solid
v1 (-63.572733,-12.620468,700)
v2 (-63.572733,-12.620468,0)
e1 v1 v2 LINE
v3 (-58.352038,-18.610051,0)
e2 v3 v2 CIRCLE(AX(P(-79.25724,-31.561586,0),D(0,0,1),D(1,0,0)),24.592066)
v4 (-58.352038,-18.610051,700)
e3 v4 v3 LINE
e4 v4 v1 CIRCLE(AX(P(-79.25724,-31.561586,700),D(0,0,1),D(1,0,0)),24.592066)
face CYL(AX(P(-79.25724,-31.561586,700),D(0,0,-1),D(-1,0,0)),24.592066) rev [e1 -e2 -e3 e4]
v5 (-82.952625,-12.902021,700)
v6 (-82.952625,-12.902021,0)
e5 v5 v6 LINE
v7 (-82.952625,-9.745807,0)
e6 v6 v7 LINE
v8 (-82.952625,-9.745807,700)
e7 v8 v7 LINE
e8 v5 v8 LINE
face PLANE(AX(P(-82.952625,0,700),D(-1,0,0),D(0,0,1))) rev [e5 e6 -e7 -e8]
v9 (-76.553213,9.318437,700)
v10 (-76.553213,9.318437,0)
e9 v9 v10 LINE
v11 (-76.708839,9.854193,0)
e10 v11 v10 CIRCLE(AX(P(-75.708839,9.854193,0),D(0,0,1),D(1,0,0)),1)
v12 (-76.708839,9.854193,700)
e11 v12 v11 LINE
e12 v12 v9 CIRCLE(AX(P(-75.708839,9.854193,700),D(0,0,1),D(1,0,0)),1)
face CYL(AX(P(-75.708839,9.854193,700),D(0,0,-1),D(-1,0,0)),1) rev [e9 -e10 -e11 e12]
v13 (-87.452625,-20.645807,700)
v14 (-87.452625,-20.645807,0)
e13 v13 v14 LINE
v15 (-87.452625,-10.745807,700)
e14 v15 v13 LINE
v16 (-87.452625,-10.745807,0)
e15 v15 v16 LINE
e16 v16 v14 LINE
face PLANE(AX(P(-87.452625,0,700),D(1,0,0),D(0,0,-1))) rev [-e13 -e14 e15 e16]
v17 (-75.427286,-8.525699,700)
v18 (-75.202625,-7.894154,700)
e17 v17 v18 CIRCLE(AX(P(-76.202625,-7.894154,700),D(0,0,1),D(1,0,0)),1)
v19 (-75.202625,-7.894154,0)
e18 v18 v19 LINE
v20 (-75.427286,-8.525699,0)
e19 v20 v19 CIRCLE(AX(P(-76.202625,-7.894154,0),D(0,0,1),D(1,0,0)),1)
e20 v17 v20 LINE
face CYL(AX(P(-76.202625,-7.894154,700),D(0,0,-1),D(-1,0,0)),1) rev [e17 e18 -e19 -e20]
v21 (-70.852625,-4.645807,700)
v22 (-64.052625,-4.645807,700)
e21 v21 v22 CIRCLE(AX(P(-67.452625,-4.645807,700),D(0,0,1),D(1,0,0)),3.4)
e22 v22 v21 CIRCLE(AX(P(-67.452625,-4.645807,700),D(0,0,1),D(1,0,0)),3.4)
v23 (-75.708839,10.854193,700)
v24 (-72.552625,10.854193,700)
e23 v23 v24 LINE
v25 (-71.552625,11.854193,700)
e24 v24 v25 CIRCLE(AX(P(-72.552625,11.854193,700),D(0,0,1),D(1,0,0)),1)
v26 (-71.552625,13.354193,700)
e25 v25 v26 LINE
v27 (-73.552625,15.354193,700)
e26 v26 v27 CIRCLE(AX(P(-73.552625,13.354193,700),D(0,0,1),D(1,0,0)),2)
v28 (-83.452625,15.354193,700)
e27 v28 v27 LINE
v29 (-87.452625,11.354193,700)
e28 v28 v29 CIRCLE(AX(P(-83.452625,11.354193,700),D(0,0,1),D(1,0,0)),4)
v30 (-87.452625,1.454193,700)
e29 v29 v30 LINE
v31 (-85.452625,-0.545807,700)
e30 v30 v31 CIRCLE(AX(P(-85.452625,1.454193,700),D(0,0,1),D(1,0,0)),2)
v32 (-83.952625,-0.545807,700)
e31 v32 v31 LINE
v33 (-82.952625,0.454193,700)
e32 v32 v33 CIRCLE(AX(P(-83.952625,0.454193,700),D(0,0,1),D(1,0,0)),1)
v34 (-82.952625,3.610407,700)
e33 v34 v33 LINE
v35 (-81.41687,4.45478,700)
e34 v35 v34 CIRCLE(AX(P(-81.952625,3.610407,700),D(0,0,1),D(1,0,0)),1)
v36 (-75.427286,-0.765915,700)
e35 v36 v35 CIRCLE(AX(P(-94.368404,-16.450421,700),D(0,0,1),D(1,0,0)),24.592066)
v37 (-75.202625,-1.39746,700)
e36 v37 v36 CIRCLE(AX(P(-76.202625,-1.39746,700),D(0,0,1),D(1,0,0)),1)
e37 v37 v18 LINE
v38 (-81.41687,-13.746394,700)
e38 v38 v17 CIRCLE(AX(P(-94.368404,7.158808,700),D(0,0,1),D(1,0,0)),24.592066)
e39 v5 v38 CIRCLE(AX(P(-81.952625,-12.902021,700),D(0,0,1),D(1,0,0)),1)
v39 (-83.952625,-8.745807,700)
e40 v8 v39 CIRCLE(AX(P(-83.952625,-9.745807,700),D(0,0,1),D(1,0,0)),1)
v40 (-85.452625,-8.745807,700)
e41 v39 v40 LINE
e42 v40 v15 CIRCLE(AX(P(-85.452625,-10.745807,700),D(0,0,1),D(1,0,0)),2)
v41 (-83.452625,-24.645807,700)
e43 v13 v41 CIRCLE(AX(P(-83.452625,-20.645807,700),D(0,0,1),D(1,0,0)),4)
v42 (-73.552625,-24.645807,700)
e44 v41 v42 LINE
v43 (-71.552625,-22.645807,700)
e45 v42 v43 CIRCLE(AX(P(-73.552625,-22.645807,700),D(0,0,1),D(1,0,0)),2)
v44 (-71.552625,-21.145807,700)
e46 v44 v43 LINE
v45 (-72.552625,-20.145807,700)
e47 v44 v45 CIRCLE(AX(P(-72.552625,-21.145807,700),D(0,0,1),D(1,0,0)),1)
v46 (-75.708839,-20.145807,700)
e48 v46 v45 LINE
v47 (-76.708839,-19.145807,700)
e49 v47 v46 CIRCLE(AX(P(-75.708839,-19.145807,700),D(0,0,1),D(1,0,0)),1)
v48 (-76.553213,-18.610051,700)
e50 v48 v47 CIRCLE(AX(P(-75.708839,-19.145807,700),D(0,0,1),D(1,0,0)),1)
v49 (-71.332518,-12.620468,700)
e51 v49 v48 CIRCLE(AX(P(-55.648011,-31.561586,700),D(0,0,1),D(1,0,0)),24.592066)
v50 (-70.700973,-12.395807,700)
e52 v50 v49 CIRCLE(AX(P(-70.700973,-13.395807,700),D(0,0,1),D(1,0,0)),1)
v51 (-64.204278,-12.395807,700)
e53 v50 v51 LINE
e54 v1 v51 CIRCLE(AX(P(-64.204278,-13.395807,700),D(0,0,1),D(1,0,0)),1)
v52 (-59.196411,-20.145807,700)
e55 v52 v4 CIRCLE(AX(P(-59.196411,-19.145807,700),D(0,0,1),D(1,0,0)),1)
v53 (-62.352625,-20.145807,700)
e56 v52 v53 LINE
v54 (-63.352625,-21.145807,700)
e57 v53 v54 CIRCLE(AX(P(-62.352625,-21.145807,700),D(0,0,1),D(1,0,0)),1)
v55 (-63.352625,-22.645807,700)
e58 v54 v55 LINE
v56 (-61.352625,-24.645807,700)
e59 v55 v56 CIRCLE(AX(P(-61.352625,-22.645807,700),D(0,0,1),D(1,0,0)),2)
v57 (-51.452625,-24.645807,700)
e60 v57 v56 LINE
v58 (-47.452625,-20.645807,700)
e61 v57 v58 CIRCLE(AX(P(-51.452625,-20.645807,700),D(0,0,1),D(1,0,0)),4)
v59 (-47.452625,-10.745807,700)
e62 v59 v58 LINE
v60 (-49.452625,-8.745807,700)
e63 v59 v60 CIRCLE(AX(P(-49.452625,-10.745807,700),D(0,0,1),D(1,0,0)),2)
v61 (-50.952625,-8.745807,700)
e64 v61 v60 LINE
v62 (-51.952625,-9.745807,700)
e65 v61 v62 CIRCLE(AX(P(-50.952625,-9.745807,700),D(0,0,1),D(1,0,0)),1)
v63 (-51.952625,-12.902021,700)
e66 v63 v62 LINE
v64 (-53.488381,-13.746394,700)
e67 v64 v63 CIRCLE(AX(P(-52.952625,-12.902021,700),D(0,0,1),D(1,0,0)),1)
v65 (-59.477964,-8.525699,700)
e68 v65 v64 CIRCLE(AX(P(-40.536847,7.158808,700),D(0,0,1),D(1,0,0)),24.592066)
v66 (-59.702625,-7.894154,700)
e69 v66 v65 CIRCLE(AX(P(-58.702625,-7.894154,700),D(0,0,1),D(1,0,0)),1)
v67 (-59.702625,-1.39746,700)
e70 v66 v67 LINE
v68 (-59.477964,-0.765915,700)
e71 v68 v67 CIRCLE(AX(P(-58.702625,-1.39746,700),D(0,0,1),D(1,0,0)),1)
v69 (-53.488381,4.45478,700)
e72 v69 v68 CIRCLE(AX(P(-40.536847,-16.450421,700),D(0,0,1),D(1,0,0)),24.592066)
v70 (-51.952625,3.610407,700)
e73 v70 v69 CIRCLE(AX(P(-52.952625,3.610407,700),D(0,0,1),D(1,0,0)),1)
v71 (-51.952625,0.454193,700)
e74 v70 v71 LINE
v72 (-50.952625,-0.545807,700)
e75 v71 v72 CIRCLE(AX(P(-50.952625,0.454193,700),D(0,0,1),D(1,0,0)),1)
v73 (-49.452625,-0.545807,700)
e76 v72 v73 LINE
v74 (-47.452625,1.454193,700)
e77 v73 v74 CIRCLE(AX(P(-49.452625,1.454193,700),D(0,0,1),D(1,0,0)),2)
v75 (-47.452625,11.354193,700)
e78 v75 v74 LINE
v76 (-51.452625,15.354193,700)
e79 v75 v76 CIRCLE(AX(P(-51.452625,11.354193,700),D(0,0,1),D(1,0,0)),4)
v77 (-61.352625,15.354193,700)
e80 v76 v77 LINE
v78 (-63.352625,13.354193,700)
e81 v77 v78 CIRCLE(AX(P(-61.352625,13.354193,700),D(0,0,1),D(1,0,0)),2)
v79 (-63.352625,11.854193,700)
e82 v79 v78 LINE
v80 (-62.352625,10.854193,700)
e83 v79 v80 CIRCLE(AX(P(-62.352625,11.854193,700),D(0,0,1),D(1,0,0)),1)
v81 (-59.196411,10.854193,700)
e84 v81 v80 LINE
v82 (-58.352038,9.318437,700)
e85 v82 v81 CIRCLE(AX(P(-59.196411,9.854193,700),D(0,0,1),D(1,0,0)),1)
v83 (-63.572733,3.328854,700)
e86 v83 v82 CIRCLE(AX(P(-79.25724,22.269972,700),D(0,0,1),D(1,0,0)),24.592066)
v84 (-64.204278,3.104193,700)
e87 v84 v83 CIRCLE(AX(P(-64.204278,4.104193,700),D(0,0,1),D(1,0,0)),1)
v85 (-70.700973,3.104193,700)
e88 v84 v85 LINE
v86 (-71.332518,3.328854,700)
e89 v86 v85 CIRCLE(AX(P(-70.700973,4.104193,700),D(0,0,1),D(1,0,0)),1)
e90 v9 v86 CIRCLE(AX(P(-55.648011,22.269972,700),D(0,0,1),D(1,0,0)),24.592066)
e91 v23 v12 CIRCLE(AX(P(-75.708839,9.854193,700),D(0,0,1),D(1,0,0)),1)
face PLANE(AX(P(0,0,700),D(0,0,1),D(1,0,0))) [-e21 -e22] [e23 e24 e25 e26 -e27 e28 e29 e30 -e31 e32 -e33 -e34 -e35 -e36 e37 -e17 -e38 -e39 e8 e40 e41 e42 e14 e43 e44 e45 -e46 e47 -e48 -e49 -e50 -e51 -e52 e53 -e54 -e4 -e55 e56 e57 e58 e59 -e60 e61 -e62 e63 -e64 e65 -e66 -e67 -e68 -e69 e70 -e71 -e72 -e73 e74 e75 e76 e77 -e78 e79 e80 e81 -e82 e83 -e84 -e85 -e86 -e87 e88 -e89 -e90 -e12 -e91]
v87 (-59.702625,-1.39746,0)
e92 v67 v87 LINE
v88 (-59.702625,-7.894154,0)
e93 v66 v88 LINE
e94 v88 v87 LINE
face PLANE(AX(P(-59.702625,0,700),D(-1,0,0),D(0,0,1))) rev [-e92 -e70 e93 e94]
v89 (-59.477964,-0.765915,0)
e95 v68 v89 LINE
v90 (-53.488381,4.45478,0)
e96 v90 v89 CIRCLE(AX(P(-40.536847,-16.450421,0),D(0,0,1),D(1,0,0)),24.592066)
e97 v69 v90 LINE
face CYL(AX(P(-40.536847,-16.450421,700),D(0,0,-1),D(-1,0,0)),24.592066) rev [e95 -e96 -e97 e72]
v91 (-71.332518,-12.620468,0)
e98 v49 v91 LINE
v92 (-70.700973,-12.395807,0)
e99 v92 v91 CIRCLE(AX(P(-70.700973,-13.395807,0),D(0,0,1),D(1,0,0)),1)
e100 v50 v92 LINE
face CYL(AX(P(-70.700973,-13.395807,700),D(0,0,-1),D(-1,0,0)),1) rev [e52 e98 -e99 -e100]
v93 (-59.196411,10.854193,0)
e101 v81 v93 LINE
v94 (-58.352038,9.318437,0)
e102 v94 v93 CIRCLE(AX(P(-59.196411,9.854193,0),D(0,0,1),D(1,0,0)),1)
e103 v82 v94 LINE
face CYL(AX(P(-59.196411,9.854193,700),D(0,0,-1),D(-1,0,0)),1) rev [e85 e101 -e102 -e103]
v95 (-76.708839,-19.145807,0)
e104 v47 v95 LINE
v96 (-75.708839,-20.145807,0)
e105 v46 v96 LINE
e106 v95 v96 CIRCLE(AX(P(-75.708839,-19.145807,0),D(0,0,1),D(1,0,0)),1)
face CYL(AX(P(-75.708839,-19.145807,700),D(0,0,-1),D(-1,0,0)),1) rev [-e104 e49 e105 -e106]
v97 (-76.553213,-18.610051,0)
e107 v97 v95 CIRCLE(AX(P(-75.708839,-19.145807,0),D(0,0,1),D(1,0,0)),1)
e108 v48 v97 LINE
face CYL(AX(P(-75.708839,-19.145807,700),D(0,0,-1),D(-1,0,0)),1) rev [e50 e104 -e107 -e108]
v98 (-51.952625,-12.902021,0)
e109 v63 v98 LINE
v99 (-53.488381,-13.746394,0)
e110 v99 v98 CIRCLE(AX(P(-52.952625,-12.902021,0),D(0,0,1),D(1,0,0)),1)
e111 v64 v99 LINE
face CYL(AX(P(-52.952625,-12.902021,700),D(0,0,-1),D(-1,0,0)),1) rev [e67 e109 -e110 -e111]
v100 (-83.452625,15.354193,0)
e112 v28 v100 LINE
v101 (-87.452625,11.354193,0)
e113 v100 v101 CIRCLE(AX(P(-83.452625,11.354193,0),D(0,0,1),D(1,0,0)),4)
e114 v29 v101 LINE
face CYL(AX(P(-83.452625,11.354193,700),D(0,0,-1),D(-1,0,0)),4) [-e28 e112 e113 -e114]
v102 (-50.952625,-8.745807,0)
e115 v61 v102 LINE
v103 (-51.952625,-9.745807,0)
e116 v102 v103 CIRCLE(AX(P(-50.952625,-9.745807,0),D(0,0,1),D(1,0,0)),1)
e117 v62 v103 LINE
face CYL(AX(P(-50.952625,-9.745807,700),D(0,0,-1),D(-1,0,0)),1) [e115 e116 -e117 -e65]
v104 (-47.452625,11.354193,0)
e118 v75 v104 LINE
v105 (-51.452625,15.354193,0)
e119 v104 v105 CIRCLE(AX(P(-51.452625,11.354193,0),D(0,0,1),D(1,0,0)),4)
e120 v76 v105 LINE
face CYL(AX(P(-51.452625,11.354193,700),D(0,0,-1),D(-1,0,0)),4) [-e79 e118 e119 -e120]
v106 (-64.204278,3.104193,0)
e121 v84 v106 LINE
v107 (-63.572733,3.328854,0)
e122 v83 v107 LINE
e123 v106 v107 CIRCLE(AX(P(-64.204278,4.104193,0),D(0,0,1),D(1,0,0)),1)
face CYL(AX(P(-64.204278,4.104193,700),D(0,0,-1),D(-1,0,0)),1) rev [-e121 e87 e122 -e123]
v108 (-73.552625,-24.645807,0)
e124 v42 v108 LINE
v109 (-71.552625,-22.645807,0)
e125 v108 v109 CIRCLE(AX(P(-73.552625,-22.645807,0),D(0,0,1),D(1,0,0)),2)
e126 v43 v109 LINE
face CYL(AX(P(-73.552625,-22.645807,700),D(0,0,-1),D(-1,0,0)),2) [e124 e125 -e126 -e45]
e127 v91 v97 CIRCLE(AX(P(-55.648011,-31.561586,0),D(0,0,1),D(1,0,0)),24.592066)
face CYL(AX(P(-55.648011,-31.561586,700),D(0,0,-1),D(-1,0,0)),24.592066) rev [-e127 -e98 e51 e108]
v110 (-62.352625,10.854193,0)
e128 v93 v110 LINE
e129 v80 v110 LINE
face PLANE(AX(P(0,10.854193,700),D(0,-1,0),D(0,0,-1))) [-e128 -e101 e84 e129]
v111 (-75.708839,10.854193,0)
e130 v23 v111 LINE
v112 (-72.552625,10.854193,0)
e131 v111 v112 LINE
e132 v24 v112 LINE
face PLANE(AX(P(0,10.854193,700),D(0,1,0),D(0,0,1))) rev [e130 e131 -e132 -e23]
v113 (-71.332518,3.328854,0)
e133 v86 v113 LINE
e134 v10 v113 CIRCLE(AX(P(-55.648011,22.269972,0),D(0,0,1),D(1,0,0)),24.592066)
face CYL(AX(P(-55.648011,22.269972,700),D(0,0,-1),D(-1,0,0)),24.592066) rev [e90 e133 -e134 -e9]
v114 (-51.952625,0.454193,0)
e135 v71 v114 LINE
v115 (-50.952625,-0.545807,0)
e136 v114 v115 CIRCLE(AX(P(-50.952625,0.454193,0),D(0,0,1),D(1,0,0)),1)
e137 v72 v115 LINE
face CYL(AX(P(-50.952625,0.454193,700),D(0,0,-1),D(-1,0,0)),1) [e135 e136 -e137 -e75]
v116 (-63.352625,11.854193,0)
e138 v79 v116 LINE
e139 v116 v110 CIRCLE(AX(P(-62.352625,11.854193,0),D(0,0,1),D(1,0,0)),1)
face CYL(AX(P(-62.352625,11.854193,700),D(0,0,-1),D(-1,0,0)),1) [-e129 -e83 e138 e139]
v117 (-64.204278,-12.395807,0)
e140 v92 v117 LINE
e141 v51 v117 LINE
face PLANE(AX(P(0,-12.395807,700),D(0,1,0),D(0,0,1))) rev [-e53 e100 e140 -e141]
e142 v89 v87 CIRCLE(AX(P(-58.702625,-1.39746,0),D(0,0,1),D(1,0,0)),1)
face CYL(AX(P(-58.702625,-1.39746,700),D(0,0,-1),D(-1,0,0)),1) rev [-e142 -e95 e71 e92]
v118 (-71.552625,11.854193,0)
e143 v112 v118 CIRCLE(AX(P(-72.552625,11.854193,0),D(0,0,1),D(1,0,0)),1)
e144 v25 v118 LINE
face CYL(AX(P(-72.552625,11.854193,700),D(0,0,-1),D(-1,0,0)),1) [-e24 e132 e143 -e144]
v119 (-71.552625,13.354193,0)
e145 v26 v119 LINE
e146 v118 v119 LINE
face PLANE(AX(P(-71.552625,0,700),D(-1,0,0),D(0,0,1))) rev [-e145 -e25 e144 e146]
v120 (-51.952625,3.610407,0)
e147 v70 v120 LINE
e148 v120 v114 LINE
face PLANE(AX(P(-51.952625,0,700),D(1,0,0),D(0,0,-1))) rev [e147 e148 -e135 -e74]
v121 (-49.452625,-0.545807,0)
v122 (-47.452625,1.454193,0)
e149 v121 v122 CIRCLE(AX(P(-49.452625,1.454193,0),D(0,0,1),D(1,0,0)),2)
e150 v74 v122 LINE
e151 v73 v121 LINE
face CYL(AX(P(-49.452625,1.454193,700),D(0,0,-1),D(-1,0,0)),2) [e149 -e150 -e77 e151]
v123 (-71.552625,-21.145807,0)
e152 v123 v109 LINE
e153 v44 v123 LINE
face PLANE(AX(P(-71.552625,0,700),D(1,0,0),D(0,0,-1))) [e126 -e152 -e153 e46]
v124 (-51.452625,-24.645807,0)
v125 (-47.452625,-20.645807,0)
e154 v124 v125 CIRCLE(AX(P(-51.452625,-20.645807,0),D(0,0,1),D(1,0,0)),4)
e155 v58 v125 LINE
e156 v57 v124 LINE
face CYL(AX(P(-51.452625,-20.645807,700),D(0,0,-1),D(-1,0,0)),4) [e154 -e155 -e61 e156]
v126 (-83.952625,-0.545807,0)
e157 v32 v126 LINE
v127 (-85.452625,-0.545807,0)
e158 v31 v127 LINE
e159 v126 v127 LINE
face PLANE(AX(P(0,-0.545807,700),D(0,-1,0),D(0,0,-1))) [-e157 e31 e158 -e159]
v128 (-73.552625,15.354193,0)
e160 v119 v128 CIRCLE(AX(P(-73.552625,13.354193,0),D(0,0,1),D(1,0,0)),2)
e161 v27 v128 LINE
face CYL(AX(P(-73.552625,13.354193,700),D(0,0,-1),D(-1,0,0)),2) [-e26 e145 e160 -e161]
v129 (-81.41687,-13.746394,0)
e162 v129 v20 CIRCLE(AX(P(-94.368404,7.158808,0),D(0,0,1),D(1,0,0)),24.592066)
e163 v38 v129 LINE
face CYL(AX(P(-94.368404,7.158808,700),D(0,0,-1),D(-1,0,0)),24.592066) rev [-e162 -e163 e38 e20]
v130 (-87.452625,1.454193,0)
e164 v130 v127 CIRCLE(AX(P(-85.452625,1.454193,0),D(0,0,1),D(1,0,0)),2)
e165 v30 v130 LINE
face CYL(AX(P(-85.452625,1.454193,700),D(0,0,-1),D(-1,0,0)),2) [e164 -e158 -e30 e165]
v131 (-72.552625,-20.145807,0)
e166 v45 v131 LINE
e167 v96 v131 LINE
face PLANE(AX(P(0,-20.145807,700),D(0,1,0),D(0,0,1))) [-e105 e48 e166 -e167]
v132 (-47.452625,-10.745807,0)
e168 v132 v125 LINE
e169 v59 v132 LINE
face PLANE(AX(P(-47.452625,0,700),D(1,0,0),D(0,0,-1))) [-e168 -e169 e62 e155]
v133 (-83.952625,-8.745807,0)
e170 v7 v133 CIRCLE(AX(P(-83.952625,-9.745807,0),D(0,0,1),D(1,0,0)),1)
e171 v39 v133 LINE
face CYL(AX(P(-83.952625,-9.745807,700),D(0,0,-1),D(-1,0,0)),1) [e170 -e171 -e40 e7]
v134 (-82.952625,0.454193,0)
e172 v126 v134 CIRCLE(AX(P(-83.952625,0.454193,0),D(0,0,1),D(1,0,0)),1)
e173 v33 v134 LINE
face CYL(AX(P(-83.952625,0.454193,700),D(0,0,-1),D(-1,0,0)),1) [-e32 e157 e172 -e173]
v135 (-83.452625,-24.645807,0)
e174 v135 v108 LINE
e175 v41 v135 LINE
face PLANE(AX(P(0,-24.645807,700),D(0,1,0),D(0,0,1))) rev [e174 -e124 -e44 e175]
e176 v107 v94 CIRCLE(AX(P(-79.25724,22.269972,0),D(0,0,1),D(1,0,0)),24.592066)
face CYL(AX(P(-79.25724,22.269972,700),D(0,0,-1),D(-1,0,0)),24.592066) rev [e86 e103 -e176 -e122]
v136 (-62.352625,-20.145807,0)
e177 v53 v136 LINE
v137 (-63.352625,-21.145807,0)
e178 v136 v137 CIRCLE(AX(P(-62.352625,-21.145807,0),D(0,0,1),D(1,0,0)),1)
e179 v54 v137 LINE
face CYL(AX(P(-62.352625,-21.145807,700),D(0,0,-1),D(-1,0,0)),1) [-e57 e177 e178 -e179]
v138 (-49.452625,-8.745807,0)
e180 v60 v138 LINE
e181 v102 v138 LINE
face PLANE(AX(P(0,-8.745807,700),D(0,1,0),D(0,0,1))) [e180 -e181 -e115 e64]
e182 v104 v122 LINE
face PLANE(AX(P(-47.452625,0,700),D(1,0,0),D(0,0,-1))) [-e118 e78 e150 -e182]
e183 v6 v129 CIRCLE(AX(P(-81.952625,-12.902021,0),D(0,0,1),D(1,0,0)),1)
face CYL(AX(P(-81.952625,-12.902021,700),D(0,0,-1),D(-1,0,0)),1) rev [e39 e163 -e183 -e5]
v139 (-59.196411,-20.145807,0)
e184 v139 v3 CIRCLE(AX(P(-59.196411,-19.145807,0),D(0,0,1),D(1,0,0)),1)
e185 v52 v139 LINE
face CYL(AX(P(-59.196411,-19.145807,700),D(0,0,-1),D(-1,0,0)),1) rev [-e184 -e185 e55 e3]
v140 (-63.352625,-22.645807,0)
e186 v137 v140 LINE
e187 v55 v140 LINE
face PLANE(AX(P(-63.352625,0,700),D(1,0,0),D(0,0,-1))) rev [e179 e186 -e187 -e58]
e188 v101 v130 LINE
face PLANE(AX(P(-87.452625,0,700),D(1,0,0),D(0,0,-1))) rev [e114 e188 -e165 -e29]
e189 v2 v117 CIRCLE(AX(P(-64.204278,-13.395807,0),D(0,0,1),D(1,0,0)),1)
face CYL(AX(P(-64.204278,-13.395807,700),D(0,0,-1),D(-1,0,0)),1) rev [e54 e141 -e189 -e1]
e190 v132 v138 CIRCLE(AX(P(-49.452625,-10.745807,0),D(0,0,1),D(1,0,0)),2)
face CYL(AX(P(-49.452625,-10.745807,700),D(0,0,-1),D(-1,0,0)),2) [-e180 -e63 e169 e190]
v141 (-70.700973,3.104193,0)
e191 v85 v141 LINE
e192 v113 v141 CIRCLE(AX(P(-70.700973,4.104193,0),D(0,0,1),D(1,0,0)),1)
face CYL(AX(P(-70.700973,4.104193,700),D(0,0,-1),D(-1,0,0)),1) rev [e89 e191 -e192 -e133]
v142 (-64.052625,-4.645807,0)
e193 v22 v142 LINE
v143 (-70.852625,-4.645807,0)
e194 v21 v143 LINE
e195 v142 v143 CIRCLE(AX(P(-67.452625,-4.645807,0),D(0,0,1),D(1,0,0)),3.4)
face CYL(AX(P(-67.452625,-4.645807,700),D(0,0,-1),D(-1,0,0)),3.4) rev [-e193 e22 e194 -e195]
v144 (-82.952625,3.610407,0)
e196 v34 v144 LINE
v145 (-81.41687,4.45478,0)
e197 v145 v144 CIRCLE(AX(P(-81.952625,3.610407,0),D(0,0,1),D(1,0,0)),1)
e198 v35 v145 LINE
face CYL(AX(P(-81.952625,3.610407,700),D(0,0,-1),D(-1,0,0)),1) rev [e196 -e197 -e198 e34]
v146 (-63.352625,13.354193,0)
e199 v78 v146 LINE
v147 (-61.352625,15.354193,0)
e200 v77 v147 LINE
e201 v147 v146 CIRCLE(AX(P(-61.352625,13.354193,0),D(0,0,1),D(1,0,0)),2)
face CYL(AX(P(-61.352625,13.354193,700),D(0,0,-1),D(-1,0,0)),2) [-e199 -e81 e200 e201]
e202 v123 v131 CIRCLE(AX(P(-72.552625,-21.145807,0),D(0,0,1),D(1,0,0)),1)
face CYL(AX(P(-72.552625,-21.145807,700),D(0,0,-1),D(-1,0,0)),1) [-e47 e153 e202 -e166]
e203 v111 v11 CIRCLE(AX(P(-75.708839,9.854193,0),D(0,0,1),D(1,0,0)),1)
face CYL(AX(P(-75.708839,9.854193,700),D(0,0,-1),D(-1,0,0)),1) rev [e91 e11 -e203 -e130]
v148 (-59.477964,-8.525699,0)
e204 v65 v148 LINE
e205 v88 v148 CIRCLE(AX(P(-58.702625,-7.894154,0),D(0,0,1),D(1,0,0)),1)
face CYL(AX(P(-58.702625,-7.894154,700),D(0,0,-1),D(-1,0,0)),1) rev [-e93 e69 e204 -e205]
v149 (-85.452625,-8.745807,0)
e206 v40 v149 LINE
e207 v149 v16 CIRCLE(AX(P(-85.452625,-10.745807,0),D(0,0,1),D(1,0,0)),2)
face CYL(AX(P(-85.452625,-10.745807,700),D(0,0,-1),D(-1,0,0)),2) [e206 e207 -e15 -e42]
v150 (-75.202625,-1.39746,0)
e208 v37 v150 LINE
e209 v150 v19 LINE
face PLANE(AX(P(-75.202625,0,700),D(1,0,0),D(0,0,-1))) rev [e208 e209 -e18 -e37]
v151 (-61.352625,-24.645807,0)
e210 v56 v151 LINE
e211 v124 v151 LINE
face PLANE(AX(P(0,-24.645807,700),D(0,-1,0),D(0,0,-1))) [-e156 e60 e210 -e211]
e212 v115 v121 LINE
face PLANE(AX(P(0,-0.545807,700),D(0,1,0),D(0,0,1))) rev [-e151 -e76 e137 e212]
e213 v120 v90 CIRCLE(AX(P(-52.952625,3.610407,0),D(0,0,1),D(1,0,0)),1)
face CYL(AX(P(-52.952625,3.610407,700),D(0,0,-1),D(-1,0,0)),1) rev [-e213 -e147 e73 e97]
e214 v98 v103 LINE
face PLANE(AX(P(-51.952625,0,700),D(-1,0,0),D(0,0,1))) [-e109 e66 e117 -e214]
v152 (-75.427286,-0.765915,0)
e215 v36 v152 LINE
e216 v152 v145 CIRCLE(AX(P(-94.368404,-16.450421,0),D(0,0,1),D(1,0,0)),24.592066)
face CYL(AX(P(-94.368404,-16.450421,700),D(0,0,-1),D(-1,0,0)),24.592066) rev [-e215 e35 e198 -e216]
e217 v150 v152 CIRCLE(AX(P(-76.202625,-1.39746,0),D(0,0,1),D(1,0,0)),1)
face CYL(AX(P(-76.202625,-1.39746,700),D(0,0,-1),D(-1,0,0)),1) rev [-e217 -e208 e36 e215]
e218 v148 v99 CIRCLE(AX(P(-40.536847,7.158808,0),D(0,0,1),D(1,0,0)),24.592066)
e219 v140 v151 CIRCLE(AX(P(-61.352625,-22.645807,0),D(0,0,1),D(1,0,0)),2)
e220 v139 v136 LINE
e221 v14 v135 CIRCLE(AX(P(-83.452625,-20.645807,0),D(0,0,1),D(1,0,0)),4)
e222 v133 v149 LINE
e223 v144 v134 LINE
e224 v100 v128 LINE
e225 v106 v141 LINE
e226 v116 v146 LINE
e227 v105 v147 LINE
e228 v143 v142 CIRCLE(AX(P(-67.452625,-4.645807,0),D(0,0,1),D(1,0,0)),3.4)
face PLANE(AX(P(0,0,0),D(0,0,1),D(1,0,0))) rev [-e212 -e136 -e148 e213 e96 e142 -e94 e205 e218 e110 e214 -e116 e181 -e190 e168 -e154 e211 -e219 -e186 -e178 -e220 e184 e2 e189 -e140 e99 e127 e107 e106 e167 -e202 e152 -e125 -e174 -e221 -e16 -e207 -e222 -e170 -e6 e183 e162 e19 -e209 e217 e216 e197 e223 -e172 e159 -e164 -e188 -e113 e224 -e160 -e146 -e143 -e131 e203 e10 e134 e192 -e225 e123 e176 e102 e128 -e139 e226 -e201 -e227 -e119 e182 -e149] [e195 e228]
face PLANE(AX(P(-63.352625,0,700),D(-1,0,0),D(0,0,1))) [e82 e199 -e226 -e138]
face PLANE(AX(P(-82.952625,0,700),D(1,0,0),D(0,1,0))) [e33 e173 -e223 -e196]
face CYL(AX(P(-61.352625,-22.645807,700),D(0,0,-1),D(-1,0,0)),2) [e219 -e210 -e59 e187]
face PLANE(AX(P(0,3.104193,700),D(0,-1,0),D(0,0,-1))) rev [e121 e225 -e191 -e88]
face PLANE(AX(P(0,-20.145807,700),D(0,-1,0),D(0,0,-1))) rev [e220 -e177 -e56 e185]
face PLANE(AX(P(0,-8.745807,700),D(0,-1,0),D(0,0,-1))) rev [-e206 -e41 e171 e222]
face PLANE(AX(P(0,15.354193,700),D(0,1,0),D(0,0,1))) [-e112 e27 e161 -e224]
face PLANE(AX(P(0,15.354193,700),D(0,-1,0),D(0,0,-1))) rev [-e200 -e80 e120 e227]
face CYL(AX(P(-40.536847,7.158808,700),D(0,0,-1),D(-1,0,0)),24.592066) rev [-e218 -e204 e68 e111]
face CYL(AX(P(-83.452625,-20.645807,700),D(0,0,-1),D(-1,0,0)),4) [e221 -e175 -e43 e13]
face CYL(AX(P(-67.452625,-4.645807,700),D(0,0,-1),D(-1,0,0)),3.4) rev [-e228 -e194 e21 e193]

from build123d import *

# Parameters (mm, degrees)
SKETCH1_R           = 3.4
BOSS_EXTRUDE1_DEPTH = 700


with BuildPart() as part:
    # Sketch1 → Boss-Extrude1 (new body)
    with BuildSketch(Plane.XY):
        with BuildLine():
            Line((-72.552625451, -20.1458069), (-75.708839475, -20.1458069))
            ThreePointArc((-75.708839475, -20.1458069), (-76.585125865, -19.62759748), (-76.55321253, -18.610051226))
            ThreePointArc((-76.55321253, -18.610051226), (-74.186362214, -15.403020453), (-71.332517782, -12.620467892))
            ThreePointArc((-71.332517782, -12.620467892), (-71.036129936, -12.453644757), (-70.700972516, -12.3958069))
            Line((-70.700972516, -12.3958069), (-67.452625451, -12.3958069))
            Line((-67.452625451, -12.3958069), (-64.204278386, -12.3958069))
            ThreePointArc((-64.204278386, -12.3958069), (-63.869120967, -12.453644757), (-63.572733121, -12.620467892))
            ThreePointArc((-63.572733121, -12.620467892), (-60.718888688, -15.403020453), (-58.352038372, -18.610051226))
            ThreePointArc((-58.352038372, -18.610051226), (-58.320125037, -19.62759748), (-59.196411427, -20.1458069))
            Line((-59.196411427, -20.1458069), (-62.352625451, -20.1458069))
            ThreePointArc((-62.352625451, -20.1458069), (-63.059732232, -20.438700119), (-63.352625451, -21.1458069))
            Line((-63.352625451, -21.1458069), (-63.352625451, -22.6458069))
            ThreePointArc((-63.352625451, -22.6458069), (-62.766839013, -24.060020463), (-61.352625451, -24.6458069))
            Line((-61.352625451, -24.6458069), (-51.452625451, -24.6458069))
            ThreePointArc((-51.452625451, -24.6458069), (-48.624198326, -23.474234025), (-47.452625451, -20.6458069))
            Line((-47.452625451, -20.6458069), (-47.452625451, -10.7458069))
            ThreePointArc((-47.452625451, -10.7458069), (-48.038411889, -9.331593338), (-49.452625451, -8.7458069))
            Line((-49.452625451, -8.7458069), (-50.952625451, -8.7458069))
            ThreePointArc((-50.952625451, -8.7458069), (-51.659732232, -9.038700119), (-51.952625451, -9.7458069))
            Line((-51.952625451, -9.7458069), (-51.952625451, -12.902020924))
            ThreePointArc((-51.952625451, -12.902020924), (-52.470834871, -13.778307314), (-53.488381126, -13.74639398))
            ThreePointArc((-53.488381126, -13.74639398), (-56.695411898, -11.379543663), (-59.477964459, -8.525699231))
            ThreePointArc((-59.477964459, -8.525699231), (-59.644787594, -8.229311385), (-59.702625451, -7.894153965))
            Line((-59.702625451, -7.894153965), (-59.702625451, -4.6458069))
            Line((-59.702625451, -4.6458069), (-59.702625451, -1.397459836))
            ThreePointArc((-59.702625451, -1.397459836), (-59.644787594, -1.062302416), (-59.477964459, -0.76591457))
            ThreePointArc((-59.477964459, -0.76591457), (-56.695411898, 2.087929862), (-53.488381126, 4.454780179))
            ThreePointArc((-53.488381126, 4.454780179), (-52.470834871, 4.486693513), (-51.952625451, 3.610407123))
            Line((-51.952625451, 3.610407123), (-51.952625451, 0.4541931))
            ThreePointArc((-51.952625451, 0.4541931), (-51.659732232, -0.252913682), (-50.952625451, -0.5458069))
            Line((-50.952625451, -0.5458069), (-49.452625451, -0.5458069))
            ThreePointArc((-49.452625451, -0.5458069), (-48.038411889, 0.039979537), (-47.452625451, 1.4541931))
            Line((-47.452625451, 1.4541931), (-47.452625451, 11.3541931))
            ThreePointArc((-47.452625451, 11.3541931), (-48.624198326, 14.182620224), (-51.452625451, 15.3541931))
            Line((-51.452625451, 15.3541931), (-61.352625451, 15.3541931))
            ThreePointArc((-61.352625451, 15.3541931), (-62.766839013, 14.768406662), (-63.352625451, 13.3541931))
            Line((-63.352625451, 13.3541931), (-63.352625451, 11.8541931))
            ThreePointArc((-63.352625451, 11.8541931), (-63.059732232, 11.147086318), (-62.352625451, 10.8541931))
            Line((-62.352625451, 10.8541931), (-59.196411427, 10.8541931))
            ThreePointArc((-59.196411427, 10.8541931), (-58.320125037, 10.335983679), (-58.352038372, 9.318437425))
            ThreePointArc((-58.352038372, 9.318437425), (-60.718888688, 6.111406652), (-63.572733121, 3.328854091))
            ThreePointArc((-63.572733121, 3.328854091), (-63.869120967, 3.162030956), (-64.204278386, 3.1041931))
            Line((-64.204278386, 3.1041931), (-67.452625451, 3.1041931))
            Line((-67.452625451, 3.1041931), (-70.700972516, 3.1041931))
            ThreePointArc((-70.700972516, 3.1041931), (-71.036129936, 3.162030956), (-71.332517782, 3.328854091))
            ThreePointArc((-71.332517782, 3.328854091), (-74.186362214, 6.111406652), (-76.55321253, 9.318437425))
            ThreePointArc((-76.55321253, 9.318437425), (-76.585125865, 10.335983679), (-75.708839475, 10.8541931))
            Line((-75.708839475, 10.8541931), (-72.552625451, 10.8541931))
            ThreePointArc((-72.552625451, 10.8541931), (-71.84551867, 11.147086318), (-71.552625451, 11.8541931))
            Line((-71.552625451, 11.8541931), (-71.552625451, 13.3541931))
            ThreePointArc((-71.552625451, 13.3541931), (-72.138411889, 14.768406662), (-73.552625451, 15.3541931))
            Line((-73.552625451, 15.3541931), (-83.452625451, 15.3541931))
            ThreePointArc((-83.452625451, 15.3541931), (-86.281052576, 14.182620224), (-87.452625451, 11.3541931))
            Line((-87.452625451, 11.3541931), (-87.452625451, 1.4541931))
            ThreePointArc((-87.452625451, 1.4541931), (-86.866839013, 0.039979537), (-85.452625451, -0.5458069))
            Line((-85.452625451, -0.5458069), (-83.952625451, -0.5458069))
            ThreePointArc((-83.952625451, -0.5458069), (-83.24551867, -0.252913682), (-82.952625451, 0.4541931))
            Line((-82.952625451, 0.4541931), (-82.952625451, 3.610407123))
            ThreePointArc((-82.952625451, 3.610407123), (-82.434416031, 4.486693513), (-81.416869776, 4.454780179))
            ThreePointArc((-81.416869776, 4.454780179), (-78.209839004, 2.087929862), (-75.427286443, -0.76591457))
            ThreePointArc((-75.427286443, -0.76591457), (-75.260463308, -1.062302416), (-75.202625451, -1.397459836))
            Line((-75.202625451, -1.397459836), (-75.202625451, -4.6458069))
            Line((-75.202625451, -4.6458069), (-75.202625451, -7.894153965))
            ThreePointArc((-75.202625451, -7.894153965), (-75.260463308, -8.229311385), (-75.427286443, -8.525699231))
            ThreePointArc((-75.427286443, -8.525699231), (-78.209839004, -11.379543663), (-81.416869776, -13.74639398))
            ThreePointArc((-81.416869776, -13.74639398), (-82.434416031, -13.778307314), (-82.952625451, -12.902020924))
            Line((-82.952625451, -12.902020924), (-82.952625451, -9.7458069))
            ThreePointArc((-82.952625451, -9.7458069), (-83.24551867, -9.038700119), (-83.952625451, -8.7458069))
            Line((-83.952625451, -8.7458069), (-85.452625451, -8.7458069))
            ThreePointArc((-85.452625451, -8.7458069), (-86.866839013, -9.331593338), (-87.452625451, -10.7458069))
            Line((-87.452625451, -10.7458069), (-87.452625451, -20.6458069))
            ThreePointArc((-87.452625451, -20.6458069), (-86.281052576, -23.474234025), (-83.452625451, -24.6458069))
            Line((-83.452625451, -24.6458069), (-73.552625451, -24.6458069))
            ThreePointArc((-73.552625451, -24.6458069), (-72.138411889, -24.060020463), (-71.552625451, -22.6458069))
            Line((-71.552625451, -22.6458069), (-71.552625451, -21.1458069))
            ThreePointArc((-71.552625451, -21.1458069), (-71.84551867, -20.438700119), (-72.552625451, -20.1458069))
        make_face()
        with Locations((-67.452625451, -4.6458069)):
            Circle(SKETCH1_R, mode=Mode.SUBTRACT)
    extrude(amount=BOSS_EXTRUDE1_DEPTH)


solid = part.part
